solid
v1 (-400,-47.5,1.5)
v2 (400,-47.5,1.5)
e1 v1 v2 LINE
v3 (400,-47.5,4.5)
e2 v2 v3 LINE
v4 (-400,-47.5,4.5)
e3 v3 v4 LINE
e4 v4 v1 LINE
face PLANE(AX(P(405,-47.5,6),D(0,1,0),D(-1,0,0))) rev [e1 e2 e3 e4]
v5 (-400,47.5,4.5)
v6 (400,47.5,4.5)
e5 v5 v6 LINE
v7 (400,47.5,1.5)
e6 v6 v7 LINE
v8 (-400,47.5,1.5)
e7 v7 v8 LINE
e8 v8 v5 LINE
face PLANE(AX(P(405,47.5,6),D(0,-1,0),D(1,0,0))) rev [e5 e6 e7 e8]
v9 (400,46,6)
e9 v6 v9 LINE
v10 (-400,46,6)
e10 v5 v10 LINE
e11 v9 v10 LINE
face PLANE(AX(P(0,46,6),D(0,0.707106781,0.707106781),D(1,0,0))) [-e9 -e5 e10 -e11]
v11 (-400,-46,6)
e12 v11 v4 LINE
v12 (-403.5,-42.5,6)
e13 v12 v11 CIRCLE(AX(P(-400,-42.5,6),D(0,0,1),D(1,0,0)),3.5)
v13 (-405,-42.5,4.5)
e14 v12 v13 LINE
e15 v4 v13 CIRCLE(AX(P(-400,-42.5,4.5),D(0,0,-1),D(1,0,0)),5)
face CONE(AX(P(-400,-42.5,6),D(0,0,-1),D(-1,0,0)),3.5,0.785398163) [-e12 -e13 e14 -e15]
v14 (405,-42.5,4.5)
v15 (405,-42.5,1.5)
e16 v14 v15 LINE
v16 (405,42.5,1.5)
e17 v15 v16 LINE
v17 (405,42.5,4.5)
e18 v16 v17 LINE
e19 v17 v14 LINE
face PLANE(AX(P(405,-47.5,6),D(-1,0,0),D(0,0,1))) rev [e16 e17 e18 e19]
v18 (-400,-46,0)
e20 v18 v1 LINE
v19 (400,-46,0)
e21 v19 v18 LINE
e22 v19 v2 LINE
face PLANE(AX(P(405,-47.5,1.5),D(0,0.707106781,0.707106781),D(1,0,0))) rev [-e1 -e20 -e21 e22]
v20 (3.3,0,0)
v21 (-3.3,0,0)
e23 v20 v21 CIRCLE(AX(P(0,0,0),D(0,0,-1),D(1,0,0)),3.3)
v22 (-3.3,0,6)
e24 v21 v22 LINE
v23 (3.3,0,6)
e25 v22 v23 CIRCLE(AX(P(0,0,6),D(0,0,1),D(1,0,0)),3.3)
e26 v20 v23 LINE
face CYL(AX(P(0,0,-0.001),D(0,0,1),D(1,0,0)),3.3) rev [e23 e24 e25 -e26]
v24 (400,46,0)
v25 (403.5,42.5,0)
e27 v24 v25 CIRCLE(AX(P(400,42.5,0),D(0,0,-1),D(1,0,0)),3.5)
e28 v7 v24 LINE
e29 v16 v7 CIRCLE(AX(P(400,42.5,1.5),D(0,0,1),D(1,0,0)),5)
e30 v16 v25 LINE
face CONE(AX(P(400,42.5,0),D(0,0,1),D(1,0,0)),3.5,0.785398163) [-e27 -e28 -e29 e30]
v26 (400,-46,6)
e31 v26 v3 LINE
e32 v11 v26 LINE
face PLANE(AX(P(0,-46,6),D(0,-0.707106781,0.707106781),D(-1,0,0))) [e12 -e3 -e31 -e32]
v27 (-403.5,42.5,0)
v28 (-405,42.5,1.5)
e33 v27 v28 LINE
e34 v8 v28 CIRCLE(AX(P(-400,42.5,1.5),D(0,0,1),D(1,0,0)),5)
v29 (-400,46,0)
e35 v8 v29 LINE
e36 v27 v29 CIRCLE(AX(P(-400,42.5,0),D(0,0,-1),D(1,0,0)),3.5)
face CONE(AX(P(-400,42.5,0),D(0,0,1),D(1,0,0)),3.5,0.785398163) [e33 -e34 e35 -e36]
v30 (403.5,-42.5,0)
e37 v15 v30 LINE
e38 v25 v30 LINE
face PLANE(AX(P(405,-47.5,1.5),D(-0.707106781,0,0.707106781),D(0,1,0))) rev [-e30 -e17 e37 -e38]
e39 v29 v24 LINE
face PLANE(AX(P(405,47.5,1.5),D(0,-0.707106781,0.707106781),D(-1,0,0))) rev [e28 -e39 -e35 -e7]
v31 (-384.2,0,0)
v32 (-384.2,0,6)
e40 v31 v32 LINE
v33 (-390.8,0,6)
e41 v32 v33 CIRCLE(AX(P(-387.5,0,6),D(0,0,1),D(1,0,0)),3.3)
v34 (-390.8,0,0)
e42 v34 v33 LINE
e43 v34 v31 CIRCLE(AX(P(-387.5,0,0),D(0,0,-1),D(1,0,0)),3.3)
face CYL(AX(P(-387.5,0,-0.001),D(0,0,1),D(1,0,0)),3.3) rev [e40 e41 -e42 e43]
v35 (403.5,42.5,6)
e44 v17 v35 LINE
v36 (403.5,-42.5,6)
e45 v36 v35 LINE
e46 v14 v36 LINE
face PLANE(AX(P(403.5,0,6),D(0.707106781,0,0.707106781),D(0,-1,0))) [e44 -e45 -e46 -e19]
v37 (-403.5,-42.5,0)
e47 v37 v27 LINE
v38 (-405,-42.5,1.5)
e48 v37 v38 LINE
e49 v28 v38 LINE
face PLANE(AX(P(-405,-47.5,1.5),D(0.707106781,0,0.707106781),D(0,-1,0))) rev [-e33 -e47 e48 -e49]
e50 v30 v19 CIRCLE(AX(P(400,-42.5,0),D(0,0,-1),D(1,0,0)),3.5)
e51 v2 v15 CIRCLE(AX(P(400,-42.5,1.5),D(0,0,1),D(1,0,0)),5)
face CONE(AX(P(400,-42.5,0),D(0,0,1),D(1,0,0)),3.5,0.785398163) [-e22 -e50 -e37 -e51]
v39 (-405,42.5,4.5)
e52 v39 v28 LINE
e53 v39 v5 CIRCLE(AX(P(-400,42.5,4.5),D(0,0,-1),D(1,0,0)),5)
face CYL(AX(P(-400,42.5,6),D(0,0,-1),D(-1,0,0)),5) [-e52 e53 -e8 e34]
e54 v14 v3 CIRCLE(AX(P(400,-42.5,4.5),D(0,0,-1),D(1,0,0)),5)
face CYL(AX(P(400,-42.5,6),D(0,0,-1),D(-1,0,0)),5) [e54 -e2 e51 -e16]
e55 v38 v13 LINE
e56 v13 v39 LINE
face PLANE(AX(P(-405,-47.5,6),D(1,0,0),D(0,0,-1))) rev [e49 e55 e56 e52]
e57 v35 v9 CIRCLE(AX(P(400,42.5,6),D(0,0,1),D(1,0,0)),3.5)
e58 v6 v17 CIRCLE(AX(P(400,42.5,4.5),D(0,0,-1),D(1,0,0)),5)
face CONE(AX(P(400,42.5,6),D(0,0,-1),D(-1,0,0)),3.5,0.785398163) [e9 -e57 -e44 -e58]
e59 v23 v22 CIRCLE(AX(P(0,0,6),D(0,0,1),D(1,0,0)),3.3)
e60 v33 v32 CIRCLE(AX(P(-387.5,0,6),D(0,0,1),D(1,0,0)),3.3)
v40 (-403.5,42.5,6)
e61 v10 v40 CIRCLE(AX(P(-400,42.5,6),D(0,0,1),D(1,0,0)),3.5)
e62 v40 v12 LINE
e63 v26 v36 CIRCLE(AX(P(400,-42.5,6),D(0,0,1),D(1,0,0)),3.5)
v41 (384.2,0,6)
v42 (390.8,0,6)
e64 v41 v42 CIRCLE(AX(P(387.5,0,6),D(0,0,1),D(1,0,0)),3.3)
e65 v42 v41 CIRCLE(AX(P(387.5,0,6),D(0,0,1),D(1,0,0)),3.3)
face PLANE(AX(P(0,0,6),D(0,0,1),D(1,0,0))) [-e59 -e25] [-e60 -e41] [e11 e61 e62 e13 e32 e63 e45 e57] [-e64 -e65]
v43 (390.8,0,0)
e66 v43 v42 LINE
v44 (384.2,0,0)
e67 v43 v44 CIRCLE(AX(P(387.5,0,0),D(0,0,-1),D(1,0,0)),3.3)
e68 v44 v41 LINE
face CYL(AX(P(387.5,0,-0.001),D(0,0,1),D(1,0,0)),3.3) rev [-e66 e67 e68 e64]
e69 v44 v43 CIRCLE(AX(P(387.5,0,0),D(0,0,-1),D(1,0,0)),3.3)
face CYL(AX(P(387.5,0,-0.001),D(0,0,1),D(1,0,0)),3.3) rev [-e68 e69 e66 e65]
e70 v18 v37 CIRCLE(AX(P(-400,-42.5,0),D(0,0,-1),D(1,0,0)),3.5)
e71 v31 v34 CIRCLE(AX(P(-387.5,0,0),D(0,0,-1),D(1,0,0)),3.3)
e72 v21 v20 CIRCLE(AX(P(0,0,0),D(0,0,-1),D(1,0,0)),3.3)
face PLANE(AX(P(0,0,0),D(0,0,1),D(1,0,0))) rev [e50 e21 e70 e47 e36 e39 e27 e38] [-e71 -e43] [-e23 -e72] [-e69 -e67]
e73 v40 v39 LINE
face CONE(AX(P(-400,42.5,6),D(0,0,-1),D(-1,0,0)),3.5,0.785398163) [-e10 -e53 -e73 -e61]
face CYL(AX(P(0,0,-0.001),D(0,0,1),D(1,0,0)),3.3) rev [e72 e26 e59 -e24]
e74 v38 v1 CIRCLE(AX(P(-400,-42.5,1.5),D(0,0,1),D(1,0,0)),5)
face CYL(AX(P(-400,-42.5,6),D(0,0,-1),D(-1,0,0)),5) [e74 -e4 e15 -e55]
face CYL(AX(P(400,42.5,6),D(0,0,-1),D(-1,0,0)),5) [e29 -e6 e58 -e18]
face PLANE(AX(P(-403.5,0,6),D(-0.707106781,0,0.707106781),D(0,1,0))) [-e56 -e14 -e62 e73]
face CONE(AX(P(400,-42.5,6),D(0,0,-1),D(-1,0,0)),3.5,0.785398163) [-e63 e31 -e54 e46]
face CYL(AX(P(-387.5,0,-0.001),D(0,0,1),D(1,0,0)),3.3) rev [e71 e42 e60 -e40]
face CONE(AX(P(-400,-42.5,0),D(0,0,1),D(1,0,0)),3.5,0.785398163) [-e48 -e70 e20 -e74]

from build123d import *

# Parameters (mm, degrees)
SKETCH1_W           = 810
SKETCH1_H           = 95
BOSS_EXTRUDE1_DEPTH = 6
FILLET1_R           = 5
CHAMFER1_SIZE       = 1.5
CUT_EXTRUDE1_REACH  = 409.82
SKETCH2_R           = 3.3


with BuildPart() as part:
    # Sketch1 → Boss-Extrude1 (new body)
    with BuildSketch(Plane.XY):
        Rectangle(SKETCH1_W, SKETCH1_H)
    extrude(amount=BOSS_EXTRUDE1_DEPTH)

    # Fillet1
    fillet1_edges = [part.edges().sort_by_distance(p)[0] for p in [
        (-405, 47.5, 3),
        (405, 47.5, 3),
        (405, -47.5, 3),
        (-405, -47.5, 3),
    ]]
    fillet(fillet1_edges, radius=FILLET1_R)

    # Chamfer1
    chamfer1_edges = [part.edges().sort_by_distance(p)[0] for p in [
        (0, 47.5, 0),
        (0, 47.5, 6),
        (-405, 0, 0),
        (405, 0, 0),
        (0, -47.5, 0),
        (-403.535533906, 46.035533906, 0),
        (-403.535533906, -46.035533906, 0),
        (403.535533906, -46.035533906, 0),
        (403.535533906, 46.035533906, 0),
        (405, 0, 6),
        (-405, 0, 6),
        (0, -47.5, 6),
        (-403.535533906, 46.035533906, 6),
        (-403.535533906, -46.035533906, 6),
        (403.535533906, -46.035533906, 6),
        (403.535533906, 46.035533906, 6),
    ]]
    chamfer(chamfer1_edges, length=CHAMFER1_SIZE)

    # Sketch2 → Cut-Extrude1 (cut, up to next)
    with BuildSketch(Plane.XY.offset(6), mode=Mode.PRIVATE) as cut_extrude1_sk1:
        with Locations((-387.5, 0)):
            Circle(SKETCH2_R)
    cut_extrude1_tool1 = extrude(cut_extrude1_sk1.sketch, amount=-CUT_EXTRUDE1_REACH, mode=Mode.PRIVATE) & part.part
    # Sketch2 → Cut-Extrude1 (cut, up to next)
    with BuildSketch(Plane.XY.offset(6), mode=Mode.PRIVATE) as cut_extrude1_sk2:
        Circle(SKETCH2_R)
    cut_extrude1_tool2 = extrude(cut_extrude1_sk2.sketch, amount=-CUT_EXTRUDE1_REACH, mode=Mode.PRIVATE) & part.part
    # Sketch2 → Cut-Extrude1 (cut, up to next)
    with BuildSketch(Plane.XY.offset(6), mode=Mode.PRIVATE) as cut_extrude1_sk3:
        with Locations((387.5, 0)):
            Circle(SKETCH2_R)
    cut_extrude1_tool3 = extrude(cut_extrude1_sk3.sketch, amount=-CUT_EXTRUDE1_REACH, mode=Mode.PRIVATE) & part.part
    add(cut_extrude1_tool1.solids().sort_by_distance((-387.5, 0, 6))[0], mode=Mode.SUBTRACT)
    add(cut_extrude1_tool2.solids().sort_by_distance((0, 0, 6))[0], mode=Mode.SUBTRACT)
    add(cut_extrude1_tool3.solids().sort_by_distance((387.5, 0, 6))[0], mode=Mode.SUBTRACT)


solid = part.part
